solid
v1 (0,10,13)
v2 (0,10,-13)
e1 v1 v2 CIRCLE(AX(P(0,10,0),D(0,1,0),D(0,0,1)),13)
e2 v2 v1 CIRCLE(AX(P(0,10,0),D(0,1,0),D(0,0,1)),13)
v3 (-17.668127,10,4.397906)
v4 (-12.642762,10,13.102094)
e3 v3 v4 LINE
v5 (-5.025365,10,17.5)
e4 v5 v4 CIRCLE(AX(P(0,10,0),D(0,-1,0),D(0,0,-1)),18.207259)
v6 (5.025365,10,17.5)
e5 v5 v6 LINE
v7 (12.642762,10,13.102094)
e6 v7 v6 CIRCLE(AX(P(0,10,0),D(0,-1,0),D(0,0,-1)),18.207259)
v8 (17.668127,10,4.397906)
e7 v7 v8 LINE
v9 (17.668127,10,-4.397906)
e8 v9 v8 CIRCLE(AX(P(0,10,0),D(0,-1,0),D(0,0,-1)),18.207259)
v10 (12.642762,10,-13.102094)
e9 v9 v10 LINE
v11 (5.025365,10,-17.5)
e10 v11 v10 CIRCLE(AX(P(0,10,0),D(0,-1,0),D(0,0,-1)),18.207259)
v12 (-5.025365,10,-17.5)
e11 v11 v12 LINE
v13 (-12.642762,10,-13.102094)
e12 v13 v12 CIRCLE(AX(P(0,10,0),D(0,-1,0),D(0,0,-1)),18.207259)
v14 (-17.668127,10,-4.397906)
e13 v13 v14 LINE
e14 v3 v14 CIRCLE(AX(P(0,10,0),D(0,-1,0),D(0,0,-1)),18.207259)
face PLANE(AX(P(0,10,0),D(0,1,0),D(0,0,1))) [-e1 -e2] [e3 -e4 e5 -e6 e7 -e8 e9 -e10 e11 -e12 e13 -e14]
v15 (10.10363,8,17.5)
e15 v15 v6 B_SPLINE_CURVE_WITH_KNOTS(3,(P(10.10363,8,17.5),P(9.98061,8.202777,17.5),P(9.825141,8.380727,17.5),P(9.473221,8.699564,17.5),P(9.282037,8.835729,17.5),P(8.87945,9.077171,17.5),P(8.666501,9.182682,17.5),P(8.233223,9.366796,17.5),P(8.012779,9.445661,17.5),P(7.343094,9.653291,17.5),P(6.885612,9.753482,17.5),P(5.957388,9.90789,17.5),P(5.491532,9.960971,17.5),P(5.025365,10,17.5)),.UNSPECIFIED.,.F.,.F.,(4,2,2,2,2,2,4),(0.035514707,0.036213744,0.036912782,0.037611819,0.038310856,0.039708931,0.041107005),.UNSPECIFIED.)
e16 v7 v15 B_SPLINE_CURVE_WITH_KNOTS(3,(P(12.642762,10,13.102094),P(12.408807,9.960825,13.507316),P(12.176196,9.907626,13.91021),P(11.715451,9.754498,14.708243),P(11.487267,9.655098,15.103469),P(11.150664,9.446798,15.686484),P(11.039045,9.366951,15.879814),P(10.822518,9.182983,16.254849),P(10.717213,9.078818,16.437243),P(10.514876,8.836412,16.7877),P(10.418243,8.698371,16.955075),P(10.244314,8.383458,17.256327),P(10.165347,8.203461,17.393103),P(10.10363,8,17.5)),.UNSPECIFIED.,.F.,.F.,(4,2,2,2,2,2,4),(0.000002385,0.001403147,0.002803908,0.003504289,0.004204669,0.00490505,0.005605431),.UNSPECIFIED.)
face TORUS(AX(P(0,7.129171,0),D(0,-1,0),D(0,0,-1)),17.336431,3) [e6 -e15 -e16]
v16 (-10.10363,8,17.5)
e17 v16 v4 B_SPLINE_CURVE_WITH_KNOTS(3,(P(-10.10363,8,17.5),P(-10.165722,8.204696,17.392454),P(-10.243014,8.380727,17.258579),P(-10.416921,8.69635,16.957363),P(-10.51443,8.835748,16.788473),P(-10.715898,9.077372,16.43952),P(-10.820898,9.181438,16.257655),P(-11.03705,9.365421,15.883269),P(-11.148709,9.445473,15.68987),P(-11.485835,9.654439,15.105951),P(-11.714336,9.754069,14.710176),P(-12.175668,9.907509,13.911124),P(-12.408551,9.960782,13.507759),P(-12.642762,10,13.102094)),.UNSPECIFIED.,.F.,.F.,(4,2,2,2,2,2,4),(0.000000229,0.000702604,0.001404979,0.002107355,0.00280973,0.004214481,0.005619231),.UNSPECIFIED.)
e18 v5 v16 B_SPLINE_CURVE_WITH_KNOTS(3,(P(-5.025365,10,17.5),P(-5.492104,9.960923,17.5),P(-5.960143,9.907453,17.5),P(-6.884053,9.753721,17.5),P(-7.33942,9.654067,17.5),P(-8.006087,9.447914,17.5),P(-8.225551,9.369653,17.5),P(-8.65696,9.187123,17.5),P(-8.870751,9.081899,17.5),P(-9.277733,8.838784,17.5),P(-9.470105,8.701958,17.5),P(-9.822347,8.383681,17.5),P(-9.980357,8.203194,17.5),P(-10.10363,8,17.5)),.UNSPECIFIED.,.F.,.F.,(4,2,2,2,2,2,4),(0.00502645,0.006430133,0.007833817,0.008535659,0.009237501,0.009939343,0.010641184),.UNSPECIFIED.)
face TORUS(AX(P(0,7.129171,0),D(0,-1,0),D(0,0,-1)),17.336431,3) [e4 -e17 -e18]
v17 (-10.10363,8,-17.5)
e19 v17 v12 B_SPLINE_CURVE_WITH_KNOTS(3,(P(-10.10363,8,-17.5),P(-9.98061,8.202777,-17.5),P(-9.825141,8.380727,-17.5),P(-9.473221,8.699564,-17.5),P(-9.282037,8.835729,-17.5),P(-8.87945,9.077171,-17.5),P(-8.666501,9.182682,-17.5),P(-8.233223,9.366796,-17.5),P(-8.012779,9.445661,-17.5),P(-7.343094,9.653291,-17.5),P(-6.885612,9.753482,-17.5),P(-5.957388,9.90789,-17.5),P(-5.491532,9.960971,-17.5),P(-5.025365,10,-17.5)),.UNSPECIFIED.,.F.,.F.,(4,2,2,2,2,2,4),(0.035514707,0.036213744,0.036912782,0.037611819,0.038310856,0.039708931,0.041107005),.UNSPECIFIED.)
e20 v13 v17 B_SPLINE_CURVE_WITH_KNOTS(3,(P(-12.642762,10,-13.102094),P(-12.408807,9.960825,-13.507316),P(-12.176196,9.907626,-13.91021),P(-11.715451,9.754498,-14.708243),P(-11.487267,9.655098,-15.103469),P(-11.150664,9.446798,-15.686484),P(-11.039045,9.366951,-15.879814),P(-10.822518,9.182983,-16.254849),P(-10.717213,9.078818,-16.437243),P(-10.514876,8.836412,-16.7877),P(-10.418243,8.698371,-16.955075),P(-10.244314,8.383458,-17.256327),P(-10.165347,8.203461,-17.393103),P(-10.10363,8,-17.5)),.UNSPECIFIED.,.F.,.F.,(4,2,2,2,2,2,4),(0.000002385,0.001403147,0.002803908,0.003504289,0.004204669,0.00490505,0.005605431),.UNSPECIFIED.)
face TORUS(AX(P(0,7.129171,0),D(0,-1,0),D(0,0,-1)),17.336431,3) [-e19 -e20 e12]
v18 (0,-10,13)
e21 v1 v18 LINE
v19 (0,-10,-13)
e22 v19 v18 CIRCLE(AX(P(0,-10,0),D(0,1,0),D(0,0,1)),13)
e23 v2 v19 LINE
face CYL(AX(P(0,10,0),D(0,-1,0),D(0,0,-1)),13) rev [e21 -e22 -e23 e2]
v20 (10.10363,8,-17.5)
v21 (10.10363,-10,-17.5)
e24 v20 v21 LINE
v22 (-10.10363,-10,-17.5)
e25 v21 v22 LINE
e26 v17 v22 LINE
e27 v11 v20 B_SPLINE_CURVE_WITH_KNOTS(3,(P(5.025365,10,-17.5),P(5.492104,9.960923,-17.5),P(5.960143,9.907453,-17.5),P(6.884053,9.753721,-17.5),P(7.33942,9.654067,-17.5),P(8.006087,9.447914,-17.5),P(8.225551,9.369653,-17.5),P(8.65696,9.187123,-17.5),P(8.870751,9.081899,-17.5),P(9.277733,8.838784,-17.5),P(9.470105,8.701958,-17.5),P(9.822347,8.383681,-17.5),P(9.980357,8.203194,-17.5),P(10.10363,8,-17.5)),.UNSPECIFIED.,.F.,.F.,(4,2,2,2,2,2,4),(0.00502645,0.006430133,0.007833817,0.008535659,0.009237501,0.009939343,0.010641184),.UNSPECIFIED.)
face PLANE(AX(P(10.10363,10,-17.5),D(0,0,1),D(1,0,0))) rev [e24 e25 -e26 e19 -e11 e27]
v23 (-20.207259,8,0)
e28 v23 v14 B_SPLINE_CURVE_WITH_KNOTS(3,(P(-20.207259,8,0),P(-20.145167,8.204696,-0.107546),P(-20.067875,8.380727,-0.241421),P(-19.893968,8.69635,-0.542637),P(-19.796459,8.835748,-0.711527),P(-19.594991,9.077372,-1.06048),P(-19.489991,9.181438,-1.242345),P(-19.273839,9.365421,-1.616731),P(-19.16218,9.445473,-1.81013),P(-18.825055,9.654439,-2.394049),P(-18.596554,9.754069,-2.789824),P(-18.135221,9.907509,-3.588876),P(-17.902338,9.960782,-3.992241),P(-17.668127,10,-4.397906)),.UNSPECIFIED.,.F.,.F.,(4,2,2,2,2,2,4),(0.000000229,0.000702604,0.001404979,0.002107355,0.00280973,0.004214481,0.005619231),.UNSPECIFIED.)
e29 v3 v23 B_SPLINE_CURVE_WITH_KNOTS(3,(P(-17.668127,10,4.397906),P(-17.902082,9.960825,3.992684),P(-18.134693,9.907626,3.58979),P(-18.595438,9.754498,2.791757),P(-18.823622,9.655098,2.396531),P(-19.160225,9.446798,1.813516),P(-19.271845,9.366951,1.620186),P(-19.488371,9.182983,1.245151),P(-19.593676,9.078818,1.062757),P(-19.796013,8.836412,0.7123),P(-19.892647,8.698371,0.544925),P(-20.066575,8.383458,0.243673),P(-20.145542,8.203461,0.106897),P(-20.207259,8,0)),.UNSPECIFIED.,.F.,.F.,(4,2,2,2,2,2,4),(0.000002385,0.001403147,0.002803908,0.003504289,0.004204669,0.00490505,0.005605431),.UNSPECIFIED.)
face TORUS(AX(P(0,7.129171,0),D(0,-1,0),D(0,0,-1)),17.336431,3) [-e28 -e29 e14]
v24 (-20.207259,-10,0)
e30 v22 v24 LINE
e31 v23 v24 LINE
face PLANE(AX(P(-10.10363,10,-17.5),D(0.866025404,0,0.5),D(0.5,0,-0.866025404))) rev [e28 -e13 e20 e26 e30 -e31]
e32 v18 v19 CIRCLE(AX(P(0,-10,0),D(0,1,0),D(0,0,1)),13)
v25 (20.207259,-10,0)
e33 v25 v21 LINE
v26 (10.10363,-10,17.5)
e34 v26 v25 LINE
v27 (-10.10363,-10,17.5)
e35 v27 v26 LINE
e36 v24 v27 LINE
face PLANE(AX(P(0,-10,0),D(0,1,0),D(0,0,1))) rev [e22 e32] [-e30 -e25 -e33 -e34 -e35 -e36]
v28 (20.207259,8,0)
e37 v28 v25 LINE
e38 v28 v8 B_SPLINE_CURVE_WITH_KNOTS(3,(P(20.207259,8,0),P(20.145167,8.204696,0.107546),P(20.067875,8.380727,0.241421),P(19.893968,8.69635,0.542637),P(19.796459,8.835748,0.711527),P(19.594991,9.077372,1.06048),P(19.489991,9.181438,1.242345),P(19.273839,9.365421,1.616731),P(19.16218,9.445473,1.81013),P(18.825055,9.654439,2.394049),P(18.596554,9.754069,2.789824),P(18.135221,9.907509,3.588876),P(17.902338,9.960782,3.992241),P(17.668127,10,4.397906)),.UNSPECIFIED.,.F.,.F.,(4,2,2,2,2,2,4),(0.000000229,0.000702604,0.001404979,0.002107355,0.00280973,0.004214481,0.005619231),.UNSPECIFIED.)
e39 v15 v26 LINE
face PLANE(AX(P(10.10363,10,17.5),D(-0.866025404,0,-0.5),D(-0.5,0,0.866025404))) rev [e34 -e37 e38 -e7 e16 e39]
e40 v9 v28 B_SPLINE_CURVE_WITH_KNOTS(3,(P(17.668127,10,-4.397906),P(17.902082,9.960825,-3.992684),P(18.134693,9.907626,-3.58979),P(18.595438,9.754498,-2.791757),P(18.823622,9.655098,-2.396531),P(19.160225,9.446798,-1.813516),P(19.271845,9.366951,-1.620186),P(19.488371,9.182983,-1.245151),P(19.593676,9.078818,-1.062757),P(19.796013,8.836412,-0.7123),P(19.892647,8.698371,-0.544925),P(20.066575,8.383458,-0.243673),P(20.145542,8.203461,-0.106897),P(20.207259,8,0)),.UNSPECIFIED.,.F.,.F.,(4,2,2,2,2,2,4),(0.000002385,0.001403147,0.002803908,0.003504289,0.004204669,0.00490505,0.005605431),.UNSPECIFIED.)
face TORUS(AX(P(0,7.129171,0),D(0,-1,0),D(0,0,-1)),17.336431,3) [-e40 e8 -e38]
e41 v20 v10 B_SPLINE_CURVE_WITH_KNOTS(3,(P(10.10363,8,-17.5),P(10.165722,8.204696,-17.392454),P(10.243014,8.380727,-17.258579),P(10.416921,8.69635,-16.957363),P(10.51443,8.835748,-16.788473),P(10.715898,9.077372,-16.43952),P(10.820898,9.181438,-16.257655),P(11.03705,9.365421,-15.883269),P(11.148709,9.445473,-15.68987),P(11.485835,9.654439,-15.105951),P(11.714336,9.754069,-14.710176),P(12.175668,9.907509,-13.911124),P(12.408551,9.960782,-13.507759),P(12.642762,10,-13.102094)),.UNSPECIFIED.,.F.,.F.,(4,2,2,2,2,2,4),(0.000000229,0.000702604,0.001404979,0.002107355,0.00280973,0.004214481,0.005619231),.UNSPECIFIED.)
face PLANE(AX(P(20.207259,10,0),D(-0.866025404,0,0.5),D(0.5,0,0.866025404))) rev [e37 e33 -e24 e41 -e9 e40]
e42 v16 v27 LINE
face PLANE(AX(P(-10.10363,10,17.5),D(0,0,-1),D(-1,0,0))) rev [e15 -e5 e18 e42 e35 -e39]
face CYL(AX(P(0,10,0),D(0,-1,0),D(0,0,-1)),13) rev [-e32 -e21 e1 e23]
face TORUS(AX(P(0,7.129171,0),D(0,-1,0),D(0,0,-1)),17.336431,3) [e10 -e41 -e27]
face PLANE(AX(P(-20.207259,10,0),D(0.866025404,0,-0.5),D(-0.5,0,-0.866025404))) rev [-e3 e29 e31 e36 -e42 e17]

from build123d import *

# Parameters (mm, degrees)
HEX_PROFILE_SKETCH_R = 13
HEX_NUT_BODY_DEPTH   = 10


with BuildPart() as part:
    # Hex Profile Sketch → Hex Nut Body (new, symmetric)
    with BuildSketch(Plane(origin=(0, 0, 0), x_dir=(1, 0, 0), z_dir=(0, 1, 0))):
        Polygon((20.207259422, 0), (10.103629711, 17.5), (-10.103629711, 17.5), (-20.207259422, 0), (-10.103629711, -17.5), (10.103629711, -17.5), align=None)
        with Locations(Location((0, 0, 0), (0, 0, 270))):
            Circle(HEX_PROFILE_SKETCH_R, mode=Mode.SUBTRACT)
    extrude(amount=HEX_NUT_BODY_DEPTH, both=True)

    # Corner Chamfer Profile → Corner Chamfer Cut (revolve, cut)
    with BuildSketch(Plane.XY):
        with BuildLine():
            Line((18.207259422, 10), (20.207259422, 10))
            Line((20.207259422, 10), (20.207259422, 8))
            ThreePointArc((20.207259422, 8), (19.457751072, 9.25049165), (18.207259422, 10))
        make_face()
    revolve(axis=Axis((0, 0, 0), (0, 1, 0)), mode=Mode.SUBTRACT)


solid = part.part
